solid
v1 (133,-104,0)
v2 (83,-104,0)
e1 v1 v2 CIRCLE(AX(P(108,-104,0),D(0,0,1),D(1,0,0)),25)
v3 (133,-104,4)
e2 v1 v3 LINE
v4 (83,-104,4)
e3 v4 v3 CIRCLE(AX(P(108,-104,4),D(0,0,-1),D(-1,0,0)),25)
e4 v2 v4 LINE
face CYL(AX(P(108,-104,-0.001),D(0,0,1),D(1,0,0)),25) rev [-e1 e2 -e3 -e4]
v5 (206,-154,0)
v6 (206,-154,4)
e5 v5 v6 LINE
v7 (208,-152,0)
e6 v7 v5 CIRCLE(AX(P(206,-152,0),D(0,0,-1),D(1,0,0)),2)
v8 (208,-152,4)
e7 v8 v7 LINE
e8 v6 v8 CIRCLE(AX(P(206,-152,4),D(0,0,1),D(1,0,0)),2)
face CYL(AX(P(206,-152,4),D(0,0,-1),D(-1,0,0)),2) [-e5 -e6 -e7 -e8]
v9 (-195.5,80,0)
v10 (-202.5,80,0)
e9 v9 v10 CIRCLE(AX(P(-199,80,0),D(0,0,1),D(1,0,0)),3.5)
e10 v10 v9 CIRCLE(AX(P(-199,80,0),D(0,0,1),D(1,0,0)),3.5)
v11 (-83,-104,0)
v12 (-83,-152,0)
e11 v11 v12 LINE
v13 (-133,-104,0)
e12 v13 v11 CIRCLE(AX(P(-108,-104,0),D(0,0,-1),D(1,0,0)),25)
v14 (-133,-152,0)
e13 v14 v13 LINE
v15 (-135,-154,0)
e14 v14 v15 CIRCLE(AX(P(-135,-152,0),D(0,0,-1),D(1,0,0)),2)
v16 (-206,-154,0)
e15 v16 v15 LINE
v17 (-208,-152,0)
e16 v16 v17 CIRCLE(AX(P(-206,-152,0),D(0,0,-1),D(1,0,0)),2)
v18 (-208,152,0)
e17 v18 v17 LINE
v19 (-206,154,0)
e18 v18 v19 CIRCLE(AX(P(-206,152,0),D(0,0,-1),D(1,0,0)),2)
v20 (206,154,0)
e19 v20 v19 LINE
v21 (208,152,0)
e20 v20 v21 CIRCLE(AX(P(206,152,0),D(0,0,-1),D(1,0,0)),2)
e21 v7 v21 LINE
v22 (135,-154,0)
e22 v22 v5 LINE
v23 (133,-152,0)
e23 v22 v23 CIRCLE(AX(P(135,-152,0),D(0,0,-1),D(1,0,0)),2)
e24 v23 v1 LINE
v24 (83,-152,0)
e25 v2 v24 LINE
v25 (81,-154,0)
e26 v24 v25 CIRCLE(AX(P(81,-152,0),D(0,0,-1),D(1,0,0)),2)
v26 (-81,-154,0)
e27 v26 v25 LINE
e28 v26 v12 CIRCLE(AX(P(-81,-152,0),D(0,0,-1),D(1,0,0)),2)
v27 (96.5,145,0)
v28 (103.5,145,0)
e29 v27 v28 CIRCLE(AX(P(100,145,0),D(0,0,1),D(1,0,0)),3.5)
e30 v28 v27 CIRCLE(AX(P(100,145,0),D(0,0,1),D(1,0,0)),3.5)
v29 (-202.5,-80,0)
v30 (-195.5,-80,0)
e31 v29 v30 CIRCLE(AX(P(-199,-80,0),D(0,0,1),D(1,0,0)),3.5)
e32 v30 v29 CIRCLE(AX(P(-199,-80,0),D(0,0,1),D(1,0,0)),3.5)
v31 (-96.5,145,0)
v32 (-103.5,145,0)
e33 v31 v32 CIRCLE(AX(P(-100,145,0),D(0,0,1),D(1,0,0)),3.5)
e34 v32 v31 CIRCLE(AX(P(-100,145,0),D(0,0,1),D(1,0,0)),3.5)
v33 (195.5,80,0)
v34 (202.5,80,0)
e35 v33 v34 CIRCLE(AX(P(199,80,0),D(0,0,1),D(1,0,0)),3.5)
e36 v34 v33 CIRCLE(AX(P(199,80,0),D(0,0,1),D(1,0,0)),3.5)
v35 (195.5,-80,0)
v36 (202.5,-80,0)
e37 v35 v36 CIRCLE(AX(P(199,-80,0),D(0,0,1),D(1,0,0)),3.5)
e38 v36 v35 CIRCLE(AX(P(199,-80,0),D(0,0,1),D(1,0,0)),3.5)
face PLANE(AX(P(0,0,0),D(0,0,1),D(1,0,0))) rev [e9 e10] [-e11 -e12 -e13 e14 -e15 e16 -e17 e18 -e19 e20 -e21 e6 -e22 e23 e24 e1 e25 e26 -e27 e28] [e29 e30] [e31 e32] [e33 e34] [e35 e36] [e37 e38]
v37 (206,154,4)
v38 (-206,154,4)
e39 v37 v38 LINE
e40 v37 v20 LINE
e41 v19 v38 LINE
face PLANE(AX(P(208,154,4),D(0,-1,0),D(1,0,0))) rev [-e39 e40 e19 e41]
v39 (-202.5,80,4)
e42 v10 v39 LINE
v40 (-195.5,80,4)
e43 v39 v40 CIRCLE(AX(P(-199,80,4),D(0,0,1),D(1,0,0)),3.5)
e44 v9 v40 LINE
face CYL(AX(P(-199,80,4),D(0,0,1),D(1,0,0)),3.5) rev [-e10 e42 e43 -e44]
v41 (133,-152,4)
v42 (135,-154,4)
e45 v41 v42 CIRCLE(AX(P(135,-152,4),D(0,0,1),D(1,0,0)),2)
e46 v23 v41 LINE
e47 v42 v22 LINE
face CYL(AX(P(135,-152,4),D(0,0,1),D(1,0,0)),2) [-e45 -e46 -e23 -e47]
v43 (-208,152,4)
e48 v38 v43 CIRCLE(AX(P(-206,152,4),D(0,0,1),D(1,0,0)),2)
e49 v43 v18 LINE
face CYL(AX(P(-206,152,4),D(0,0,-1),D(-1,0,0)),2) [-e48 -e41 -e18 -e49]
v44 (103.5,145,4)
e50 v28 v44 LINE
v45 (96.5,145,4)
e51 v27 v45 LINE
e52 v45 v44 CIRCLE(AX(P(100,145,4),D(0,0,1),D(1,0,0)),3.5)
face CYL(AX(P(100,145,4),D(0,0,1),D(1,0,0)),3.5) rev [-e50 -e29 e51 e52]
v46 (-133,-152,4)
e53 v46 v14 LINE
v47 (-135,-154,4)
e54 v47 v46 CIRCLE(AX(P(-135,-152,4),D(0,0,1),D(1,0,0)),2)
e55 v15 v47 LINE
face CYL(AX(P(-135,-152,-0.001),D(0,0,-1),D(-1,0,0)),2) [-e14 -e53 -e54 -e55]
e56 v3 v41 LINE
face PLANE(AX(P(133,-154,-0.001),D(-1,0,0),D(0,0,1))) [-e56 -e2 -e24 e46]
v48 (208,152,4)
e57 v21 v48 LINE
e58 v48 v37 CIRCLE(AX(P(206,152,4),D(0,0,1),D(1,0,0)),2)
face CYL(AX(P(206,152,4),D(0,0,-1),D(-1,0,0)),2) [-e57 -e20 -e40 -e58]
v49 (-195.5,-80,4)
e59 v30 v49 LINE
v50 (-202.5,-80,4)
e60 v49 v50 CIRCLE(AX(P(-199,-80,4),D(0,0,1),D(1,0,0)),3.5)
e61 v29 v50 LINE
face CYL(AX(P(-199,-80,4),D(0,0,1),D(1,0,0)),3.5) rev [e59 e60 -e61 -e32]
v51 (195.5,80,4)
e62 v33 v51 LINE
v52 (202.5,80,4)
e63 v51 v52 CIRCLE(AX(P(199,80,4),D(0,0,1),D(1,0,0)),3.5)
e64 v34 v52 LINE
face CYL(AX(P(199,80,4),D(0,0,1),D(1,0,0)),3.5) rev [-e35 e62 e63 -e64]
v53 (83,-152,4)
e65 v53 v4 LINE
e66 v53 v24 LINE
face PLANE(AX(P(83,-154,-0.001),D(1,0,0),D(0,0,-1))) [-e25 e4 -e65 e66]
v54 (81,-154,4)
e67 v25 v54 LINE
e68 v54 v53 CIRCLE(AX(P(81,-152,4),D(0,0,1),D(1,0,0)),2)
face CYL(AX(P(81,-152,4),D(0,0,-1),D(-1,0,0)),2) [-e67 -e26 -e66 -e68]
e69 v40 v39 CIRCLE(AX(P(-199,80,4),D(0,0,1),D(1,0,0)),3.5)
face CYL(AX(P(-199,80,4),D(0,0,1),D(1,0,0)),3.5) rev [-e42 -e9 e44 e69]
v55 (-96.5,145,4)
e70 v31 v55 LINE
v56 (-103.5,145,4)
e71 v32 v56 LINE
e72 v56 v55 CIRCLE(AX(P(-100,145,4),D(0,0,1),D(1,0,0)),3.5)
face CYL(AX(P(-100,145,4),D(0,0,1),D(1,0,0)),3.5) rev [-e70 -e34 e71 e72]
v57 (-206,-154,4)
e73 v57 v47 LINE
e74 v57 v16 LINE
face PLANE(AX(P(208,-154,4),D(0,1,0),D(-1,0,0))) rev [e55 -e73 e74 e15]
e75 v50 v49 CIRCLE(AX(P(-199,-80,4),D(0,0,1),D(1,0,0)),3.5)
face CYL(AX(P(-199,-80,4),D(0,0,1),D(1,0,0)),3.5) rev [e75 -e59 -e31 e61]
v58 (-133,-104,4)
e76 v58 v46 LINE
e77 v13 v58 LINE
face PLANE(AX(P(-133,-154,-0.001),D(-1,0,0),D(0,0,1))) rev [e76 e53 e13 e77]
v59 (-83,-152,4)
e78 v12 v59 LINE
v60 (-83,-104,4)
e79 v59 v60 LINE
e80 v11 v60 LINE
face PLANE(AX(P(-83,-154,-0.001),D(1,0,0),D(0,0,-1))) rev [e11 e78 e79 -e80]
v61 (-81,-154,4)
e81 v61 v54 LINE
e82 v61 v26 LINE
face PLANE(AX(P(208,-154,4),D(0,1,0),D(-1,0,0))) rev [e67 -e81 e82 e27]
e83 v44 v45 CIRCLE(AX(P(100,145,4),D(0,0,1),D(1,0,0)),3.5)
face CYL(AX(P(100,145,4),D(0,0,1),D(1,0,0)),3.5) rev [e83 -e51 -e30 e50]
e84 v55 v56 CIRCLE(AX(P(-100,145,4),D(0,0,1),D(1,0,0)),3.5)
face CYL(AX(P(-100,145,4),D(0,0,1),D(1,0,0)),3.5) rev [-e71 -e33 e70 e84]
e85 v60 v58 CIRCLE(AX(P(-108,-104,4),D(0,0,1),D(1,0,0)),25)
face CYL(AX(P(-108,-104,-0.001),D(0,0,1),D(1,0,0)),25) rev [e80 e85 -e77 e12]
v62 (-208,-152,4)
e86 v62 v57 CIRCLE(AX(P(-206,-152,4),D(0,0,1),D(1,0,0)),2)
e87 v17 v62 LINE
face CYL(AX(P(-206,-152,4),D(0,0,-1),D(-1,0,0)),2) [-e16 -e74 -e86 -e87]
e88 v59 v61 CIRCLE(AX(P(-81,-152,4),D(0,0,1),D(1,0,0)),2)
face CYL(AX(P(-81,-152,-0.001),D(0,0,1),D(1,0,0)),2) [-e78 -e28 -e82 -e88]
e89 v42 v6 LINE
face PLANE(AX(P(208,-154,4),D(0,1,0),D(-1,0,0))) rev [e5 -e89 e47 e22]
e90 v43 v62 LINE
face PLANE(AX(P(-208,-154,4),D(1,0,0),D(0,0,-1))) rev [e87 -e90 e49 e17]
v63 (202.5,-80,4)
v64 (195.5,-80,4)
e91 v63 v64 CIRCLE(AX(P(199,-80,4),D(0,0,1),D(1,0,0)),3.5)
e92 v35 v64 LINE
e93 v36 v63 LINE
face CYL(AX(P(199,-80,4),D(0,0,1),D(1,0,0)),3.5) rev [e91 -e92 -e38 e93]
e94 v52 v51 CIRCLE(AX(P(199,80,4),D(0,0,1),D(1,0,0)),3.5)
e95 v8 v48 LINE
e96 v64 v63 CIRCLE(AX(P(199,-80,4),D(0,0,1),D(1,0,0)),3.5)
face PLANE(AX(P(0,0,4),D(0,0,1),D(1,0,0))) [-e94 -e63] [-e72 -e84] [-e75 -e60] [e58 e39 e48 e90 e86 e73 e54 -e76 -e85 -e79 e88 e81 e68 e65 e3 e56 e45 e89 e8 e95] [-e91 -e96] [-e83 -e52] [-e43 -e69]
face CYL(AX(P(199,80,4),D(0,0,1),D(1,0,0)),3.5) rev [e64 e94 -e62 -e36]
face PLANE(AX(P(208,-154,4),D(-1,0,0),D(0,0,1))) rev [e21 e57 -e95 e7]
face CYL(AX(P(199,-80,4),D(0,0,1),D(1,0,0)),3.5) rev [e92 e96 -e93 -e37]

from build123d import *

# Parameters (mm, degrees)
SKETCH_1_W          = 416
SKETCH_1_H          = 308
EXTRUDE_1_DEPTH     = 4
FILLET_1_R          = 2
CUT_EXTRUDE_1_REACH = 260.836
FILLET_2_R          = 2
HOLE_WIZARD_M6_1_D  = 7
HOLE_WIZARD_M6_2_D  = 7


with BuildPart() as part:
    # 草图1 → 凸台-拉伸1 (new body)
    with BuildSketch(Plane.XY):
        Rectangle(SKETCH_1_W, SKETCH_1_H)
    extrude(amount=EXTRUDE_1_DEPTH)

    # 圆角1
    fillet_1_edges = [part.edges().sort_by_distance(p)[0] for p in [
        (-208, 154, 2),
        (208, 154, 2),
        (208, -154, 2),
        (-208, -154, 2),
    ]]
    fillet(fillet_1_edges, radius=FILLET_1_R)

    # 草图2 → 切除-拉伸1 (cut, up to next)
    with BuildSketch(Plane.XY.offset(4), mode=Mode.PRIVATE) as cut_extrude_1_sk1:
        with BuildLine():
            Line((-133, -154), (-133, -104))
            ThreePointArc((-133, -104), (-108, -79), (-83, -104))
            Line((-83, -104), (-83, -154))
            ThreePointArc((-83, -154), (-108, -179), (-133, -154))
        make_face()
    cut_extrude_1_tool1 = extrude(cut_extrude_1_sk1.sketch, amount=-CUT_EXTRUDE_1_REACH, mode=Mode.PRIVATE) & part.part
    cut_extrude_1 = cut_extrude_1_tool1.solids().sort_by_distance((-108, -129, 4))[0]
    add(cut_extrude_1, mode=Mode.SUBTRACT)

    # 镜向1: 切除-拉伸1 across plane
    add(cut_extrude_1.mirror(Plane(origin=(0, 0, 0), x_dir=(0, 0, 1), z_dir=(1, 0, 0))), mode=Mode.SUBTRACT)

    # 圆角2
    fillet_2_edges = [part.edges().sort_by_distance(p)[0] for p in [
        (-133, -154, 2),
        (-83, -154, 2),
        (83, -154, 2),
        (133, -154, 2),
    ]]
    fillet(fillet_2_edges, radius=FILLET_2_R)

    # M6 间隙孔1 (through all)
    with Locations(Plane.XY.offset(4)):
        with Locations((-199, 80), (-199, -80)):
            hole_wizard_m6_1 = Hole(HOLE_WIZARD_M6_1_D / 2)

    # 镜向2: M6 间隙孔1 across plane
    add(hole_wizard_m6_1.mirror(Plane(origin=(0, 0, 0), x_dir=(0, 0, 1), z_dir=(1, 0, 0))), mode=Mode.SUBTRACT)

    # M6 间隙孔2 (through all)
    with Locations(Plane.XY.offset(4)):
        with Locations((-100, 145), (100, 145)):
            Hole(HOLE_WIZARD_M6_2_D / 2)


solid = part.part
